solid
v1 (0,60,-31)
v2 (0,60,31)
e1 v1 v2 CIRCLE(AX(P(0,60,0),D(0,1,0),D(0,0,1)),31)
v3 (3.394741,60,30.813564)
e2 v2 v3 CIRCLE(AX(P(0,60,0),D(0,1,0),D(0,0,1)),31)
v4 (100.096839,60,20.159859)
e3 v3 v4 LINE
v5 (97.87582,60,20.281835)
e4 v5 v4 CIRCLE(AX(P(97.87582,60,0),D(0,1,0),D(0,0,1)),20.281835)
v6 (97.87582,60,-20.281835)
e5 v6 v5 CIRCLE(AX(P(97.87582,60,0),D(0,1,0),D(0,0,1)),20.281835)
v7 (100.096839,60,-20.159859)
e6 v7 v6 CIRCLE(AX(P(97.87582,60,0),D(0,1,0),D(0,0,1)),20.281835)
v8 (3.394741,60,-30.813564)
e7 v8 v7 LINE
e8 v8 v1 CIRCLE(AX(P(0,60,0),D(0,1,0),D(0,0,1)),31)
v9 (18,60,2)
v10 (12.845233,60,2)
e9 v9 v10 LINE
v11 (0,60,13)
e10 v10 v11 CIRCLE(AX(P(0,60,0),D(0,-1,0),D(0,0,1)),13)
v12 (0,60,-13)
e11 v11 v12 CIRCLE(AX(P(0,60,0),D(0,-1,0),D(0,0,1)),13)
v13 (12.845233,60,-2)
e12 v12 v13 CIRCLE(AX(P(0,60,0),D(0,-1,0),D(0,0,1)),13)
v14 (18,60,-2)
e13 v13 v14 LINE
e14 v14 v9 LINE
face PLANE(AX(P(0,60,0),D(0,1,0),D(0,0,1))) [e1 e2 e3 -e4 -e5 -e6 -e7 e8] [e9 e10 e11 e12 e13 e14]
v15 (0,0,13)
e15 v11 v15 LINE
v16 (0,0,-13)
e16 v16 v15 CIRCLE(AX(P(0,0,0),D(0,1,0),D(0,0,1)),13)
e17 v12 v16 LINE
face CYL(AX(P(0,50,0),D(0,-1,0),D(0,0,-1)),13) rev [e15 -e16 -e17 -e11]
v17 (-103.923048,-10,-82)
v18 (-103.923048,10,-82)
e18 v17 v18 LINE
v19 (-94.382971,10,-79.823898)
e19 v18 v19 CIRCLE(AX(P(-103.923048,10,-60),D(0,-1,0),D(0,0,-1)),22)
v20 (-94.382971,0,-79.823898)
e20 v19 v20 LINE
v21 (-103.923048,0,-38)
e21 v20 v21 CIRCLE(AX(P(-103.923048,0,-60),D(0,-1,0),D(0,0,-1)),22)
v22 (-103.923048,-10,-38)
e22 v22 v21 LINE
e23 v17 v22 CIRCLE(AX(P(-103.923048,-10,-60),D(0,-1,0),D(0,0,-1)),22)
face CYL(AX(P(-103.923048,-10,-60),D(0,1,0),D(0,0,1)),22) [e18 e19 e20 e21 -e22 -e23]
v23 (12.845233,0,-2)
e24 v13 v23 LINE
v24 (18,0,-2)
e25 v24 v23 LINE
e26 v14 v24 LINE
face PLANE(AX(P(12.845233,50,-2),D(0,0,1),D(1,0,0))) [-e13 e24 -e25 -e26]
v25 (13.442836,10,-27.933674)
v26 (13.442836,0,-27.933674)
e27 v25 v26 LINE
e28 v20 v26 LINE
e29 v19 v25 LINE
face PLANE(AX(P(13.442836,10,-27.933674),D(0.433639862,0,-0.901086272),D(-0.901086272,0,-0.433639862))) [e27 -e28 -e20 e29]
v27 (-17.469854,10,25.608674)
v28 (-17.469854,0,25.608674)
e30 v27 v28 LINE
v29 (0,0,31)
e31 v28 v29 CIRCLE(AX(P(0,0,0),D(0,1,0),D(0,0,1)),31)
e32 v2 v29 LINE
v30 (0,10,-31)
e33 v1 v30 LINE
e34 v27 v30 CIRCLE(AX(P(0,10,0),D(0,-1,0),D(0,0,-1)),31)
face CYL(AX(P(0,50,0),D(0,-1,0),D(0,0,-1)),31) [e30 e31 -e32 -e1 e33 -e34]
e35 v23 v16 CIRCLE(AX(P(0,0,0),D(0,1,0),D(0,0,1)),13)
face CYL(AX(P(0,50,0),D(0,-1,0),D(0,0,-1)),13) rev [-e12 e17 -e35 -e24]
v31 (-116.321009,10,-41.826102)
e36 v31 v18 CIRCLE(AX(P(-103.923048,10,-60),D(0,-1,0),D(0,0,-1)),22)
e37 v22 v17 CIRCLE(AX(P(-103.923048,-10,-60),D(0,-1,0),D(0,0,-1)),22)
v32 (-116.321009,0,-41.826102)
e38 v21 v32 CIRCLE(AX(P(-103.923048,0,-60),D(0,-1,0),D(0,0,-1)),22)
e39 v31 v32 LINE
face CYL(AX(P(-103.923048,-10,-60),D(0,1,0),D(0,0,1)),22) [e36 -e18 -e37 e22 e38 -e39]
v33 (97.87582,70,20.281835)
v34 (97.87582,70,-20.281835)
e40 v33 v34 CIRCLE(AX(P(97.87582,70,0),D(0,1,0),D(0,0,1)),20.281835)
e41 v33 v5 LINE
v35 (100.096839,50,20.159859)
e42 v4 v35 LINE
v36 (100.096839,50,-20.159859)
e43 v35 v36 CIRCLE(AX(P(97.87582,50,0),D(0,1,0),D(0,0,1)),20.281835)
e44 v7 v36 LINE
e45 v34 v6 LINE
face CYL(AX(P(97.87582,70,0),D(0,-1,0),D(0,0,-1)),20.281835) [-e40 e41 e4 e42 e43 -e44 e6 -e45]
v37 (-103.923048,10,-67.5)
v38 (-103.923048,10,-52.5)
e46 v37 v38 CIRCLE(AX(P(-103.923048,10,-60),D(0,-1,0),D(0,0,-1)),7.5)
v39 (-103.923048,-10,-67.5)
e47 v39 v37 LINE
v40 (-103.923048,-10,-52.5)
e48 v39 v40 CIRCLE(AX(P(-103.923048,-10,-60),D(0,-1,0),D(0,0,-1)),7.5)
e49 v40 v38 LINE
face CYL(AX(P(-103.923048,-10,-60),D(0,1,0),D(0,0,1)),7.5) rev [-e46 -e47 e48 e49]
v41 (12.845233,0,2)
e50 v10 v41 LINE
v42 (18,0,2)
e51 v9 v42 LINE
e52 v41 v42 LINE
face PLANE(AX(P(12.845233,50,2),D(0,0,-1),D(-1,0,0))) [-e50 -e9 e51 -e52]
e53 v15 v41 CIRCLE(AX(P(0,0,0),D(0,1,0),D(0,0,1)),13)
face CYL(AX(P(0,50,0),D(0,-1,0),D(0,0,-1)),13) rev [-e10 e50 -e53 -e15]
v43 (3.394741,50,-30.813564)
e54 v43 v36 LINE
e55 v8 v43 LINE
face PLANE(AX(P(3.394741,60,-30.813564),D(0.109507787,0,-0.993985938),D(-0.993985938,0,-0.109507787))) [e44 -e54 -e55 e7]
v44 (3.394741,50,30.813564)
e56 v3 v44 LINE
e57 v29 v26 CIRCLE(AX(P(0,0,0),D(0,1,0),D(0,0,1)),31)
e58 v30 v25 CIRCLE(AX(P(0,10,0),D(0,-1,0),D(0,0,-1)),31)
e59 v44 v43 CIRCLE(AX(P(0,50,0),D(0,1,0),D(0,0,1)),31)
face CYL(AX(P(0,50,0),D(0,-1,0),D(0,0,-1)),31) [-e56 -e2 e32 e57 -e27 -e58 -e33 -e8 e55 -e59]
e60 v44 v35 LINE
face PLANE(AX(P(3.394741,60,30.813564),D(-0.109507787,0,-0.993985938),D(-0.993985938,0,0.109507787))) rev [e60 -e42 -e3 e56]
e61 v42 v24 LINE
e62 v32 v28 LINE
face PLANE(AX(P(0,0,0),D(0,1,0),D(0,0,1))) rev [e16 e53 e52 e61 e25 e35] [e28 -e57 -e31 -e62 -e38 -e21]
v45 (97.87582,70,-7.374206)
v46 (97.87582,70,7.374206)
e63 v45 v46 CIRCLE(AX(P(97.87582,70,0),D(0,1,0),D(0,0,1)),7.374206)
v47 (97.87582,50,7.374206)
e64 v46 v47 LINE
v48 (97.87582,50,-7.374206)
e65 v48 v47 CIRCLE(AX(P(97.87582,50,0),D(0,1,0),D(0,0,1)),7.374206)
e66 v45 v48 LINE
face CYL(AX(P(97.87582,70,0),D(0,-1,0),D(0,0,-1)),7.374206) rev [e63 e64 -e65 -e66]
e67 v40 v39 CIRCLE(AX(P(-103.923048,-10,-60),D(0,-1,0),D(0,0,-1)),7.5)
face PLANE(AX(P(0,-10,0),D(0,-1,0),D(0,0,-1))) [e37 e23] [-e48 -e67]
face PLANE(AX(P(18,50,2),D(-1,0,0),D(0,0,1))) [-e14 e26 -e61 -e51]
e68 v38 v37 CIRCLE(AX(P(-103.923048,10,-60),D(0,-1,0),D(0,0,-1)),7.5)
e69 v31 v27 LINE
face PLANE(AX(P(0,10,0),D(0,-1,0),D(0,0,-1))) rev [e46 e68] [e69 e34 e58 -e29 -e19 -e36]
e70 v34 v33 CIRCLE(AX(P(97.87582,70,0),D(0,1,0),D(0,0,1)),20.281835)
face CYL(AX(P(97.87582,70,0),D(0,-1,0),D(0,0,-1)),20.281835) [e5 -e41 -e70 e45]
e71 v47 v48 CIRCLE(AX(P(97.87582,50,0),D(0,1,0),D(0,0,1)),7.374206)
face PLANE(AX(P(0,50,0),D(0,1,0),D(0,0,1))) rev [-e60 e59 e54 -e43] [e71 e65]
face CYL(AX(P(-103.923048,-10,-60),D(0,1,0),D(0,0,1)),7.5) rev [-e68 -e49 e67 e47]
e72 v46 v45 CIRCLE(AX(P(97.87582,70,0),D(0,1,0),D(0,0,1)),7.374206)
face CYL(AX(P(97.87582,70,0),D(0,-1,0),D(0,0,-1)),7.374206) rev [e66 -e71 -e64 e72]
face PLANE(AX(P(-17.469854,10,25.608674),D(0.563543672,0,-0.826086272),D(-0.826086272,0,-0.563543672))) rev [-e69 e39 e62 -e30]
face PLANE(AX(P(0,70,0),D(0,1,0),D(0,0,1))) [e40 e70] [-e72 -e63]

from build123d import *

# Parameters (mm, degrees)
HUB_PROFILE_SKETCH_R       = 31
HUB_62_KEYED_BORE_26_DEPTH = 50
ARM_A_PLATE_DEPTH          = 10
SKETCH2_4_R                = 20.281835497
SKETCH2_4_R_2              = 7.37420564
ARM_A_END_BOSS_DEPTH       = 20
ARM_B_PLATE_DEPTH          = 10
ARM_B_END_BOSS_DEPTH       = 10
ARM_B_END_BOSS_DEPTH_BACK  = 10
SKETCH4_3_R                = 22
SKETCH4_3_R_2              = 7.5


with BuildPart() as part:
    # Hub Profile Sketch → Hub _62 Keyed Bore _26 (new body)
    with BuildSketch(Plane(origin=(0, 0, 0), x_dir=(1, 0, 0), z_dir=(0, 1, 0))):
        with Locations(Location((0, 0, 0), (0, 0, 270))):
            Circle(HUB_PROFILE_SKETCH_R)
        with BuildLine():
            Line((12.845232579, -2), (18, -2))
            Line((18, -2), (18, 2))
            Line((18, 2), (12.845232579, 2))
            ThreePointArc((12.845232579, 2), (-13, 0), (12.845232579, -2))
        make_face(mode=Mode.SUBTRACT)
    extrude(amount=HUB_62_KEYED_BORE_26_DEPTH)

    # Arm A Sketch → Arm A Plate (add)
    with BuildSketch(Plane(origin=(0, 50, 0), x_dir=(1, 0, 0), z_dir=(0, 1, 0))):
        with BuildLine():
            ThreePointArc((3.394741403, 30.813564072), (-31, 0), (3.394741403, -30.813564072))
            Line((3.394741403, -30.813564072), (100.096839243, -20.159859277))
            ThreePointArc((100.096839243, -20.159859277), (77.593984821, 0), (100.096839243, 20.159859277))
            Line((100.096839243, 20.159859277), (3.394741403, 30.813564072))
        make_face()
        with BuildLine():
            Line((18, 2), (18, 0))
            Line((18, 0), (18, -2))
            Line((18, -2), (12.845232579, -2))
            ThreePointArc((12.845232579, -2), (-13, 0), (12.845232579, 2))
            Line((12.845232579, 2), (18, 2))
        make_face(mode=Mode.SUBTRACT)
    extrude(amount=ARM_A_PLATE_DEPTH)

    # Sketch2_4 → Arm A End Boss (add)
    with BuildSketch(Plane(origin=(0, 50, 0), x_dir=(1, 0, 0), z_dir=(0, 1, 0))):
        with Locations(Location((97.875820318, 0, 0), (0, 0, 83.713057555))):
            Circle(SKETCH2_4_R)
        with Locations(Location((97.875820318, 0, 0), (0, 0, 270))):
            Circle(SKETCH2_4_R_2, mode=Mode.SUBTRACT)
    extrude(amount=ARM_A_END_BOSS_DEPTH)

    # Arm B Sketch → Arm B Plate (add)
    with BuildSketch(Plane.XZ):
        with BuildLine():
            Line((-17.469853837, 25.608674447), (-116.321009242, -41.826102006))
            ThreePointArc((-116.321009242, -41.826102006), (-93.645771026, -40.54807031), (-81.923048454, -60))
            ThreePointArc((-81.923048454, -60), (-85.296700275, -71.70722655), (-94.382971499, -79.823897994))
            Line((-94.382971499, -79.823897994), (13.442835709, -27.933674447))
            ThreePointArc((13.442835709, -27.933674447), (-26.846787517, -15.5), (-17.469853837, 25.608674447))
        make_face()
    extrude(amount=-ARM_B_PLATE_DEPTH)

    # Sketch4_3 → Arm B End Boss (add, two sides: drawn at the far end of the back side and taken through both)
    with BuildSketch(Plane.XZ.offset(-ARM_B_END_BOSS_DEPTH_BACK)):
        with Locations(Location((-103.923048454, -60, 0), (0, 0, 124.301222305))):
            Circle(SKETCH4_3_R)
        with Locations(Location((-103.923048454, -60, 0), (0, 0, 270))):
            Circle(SKETCH4_3_R_2, mode=Mode.SUBTRACT)
    extrude(amount=ARM_B_END_BOSS_DEPTH + ARM_B_END_BOSS_DEPTH_BACK)


solid = part.part
